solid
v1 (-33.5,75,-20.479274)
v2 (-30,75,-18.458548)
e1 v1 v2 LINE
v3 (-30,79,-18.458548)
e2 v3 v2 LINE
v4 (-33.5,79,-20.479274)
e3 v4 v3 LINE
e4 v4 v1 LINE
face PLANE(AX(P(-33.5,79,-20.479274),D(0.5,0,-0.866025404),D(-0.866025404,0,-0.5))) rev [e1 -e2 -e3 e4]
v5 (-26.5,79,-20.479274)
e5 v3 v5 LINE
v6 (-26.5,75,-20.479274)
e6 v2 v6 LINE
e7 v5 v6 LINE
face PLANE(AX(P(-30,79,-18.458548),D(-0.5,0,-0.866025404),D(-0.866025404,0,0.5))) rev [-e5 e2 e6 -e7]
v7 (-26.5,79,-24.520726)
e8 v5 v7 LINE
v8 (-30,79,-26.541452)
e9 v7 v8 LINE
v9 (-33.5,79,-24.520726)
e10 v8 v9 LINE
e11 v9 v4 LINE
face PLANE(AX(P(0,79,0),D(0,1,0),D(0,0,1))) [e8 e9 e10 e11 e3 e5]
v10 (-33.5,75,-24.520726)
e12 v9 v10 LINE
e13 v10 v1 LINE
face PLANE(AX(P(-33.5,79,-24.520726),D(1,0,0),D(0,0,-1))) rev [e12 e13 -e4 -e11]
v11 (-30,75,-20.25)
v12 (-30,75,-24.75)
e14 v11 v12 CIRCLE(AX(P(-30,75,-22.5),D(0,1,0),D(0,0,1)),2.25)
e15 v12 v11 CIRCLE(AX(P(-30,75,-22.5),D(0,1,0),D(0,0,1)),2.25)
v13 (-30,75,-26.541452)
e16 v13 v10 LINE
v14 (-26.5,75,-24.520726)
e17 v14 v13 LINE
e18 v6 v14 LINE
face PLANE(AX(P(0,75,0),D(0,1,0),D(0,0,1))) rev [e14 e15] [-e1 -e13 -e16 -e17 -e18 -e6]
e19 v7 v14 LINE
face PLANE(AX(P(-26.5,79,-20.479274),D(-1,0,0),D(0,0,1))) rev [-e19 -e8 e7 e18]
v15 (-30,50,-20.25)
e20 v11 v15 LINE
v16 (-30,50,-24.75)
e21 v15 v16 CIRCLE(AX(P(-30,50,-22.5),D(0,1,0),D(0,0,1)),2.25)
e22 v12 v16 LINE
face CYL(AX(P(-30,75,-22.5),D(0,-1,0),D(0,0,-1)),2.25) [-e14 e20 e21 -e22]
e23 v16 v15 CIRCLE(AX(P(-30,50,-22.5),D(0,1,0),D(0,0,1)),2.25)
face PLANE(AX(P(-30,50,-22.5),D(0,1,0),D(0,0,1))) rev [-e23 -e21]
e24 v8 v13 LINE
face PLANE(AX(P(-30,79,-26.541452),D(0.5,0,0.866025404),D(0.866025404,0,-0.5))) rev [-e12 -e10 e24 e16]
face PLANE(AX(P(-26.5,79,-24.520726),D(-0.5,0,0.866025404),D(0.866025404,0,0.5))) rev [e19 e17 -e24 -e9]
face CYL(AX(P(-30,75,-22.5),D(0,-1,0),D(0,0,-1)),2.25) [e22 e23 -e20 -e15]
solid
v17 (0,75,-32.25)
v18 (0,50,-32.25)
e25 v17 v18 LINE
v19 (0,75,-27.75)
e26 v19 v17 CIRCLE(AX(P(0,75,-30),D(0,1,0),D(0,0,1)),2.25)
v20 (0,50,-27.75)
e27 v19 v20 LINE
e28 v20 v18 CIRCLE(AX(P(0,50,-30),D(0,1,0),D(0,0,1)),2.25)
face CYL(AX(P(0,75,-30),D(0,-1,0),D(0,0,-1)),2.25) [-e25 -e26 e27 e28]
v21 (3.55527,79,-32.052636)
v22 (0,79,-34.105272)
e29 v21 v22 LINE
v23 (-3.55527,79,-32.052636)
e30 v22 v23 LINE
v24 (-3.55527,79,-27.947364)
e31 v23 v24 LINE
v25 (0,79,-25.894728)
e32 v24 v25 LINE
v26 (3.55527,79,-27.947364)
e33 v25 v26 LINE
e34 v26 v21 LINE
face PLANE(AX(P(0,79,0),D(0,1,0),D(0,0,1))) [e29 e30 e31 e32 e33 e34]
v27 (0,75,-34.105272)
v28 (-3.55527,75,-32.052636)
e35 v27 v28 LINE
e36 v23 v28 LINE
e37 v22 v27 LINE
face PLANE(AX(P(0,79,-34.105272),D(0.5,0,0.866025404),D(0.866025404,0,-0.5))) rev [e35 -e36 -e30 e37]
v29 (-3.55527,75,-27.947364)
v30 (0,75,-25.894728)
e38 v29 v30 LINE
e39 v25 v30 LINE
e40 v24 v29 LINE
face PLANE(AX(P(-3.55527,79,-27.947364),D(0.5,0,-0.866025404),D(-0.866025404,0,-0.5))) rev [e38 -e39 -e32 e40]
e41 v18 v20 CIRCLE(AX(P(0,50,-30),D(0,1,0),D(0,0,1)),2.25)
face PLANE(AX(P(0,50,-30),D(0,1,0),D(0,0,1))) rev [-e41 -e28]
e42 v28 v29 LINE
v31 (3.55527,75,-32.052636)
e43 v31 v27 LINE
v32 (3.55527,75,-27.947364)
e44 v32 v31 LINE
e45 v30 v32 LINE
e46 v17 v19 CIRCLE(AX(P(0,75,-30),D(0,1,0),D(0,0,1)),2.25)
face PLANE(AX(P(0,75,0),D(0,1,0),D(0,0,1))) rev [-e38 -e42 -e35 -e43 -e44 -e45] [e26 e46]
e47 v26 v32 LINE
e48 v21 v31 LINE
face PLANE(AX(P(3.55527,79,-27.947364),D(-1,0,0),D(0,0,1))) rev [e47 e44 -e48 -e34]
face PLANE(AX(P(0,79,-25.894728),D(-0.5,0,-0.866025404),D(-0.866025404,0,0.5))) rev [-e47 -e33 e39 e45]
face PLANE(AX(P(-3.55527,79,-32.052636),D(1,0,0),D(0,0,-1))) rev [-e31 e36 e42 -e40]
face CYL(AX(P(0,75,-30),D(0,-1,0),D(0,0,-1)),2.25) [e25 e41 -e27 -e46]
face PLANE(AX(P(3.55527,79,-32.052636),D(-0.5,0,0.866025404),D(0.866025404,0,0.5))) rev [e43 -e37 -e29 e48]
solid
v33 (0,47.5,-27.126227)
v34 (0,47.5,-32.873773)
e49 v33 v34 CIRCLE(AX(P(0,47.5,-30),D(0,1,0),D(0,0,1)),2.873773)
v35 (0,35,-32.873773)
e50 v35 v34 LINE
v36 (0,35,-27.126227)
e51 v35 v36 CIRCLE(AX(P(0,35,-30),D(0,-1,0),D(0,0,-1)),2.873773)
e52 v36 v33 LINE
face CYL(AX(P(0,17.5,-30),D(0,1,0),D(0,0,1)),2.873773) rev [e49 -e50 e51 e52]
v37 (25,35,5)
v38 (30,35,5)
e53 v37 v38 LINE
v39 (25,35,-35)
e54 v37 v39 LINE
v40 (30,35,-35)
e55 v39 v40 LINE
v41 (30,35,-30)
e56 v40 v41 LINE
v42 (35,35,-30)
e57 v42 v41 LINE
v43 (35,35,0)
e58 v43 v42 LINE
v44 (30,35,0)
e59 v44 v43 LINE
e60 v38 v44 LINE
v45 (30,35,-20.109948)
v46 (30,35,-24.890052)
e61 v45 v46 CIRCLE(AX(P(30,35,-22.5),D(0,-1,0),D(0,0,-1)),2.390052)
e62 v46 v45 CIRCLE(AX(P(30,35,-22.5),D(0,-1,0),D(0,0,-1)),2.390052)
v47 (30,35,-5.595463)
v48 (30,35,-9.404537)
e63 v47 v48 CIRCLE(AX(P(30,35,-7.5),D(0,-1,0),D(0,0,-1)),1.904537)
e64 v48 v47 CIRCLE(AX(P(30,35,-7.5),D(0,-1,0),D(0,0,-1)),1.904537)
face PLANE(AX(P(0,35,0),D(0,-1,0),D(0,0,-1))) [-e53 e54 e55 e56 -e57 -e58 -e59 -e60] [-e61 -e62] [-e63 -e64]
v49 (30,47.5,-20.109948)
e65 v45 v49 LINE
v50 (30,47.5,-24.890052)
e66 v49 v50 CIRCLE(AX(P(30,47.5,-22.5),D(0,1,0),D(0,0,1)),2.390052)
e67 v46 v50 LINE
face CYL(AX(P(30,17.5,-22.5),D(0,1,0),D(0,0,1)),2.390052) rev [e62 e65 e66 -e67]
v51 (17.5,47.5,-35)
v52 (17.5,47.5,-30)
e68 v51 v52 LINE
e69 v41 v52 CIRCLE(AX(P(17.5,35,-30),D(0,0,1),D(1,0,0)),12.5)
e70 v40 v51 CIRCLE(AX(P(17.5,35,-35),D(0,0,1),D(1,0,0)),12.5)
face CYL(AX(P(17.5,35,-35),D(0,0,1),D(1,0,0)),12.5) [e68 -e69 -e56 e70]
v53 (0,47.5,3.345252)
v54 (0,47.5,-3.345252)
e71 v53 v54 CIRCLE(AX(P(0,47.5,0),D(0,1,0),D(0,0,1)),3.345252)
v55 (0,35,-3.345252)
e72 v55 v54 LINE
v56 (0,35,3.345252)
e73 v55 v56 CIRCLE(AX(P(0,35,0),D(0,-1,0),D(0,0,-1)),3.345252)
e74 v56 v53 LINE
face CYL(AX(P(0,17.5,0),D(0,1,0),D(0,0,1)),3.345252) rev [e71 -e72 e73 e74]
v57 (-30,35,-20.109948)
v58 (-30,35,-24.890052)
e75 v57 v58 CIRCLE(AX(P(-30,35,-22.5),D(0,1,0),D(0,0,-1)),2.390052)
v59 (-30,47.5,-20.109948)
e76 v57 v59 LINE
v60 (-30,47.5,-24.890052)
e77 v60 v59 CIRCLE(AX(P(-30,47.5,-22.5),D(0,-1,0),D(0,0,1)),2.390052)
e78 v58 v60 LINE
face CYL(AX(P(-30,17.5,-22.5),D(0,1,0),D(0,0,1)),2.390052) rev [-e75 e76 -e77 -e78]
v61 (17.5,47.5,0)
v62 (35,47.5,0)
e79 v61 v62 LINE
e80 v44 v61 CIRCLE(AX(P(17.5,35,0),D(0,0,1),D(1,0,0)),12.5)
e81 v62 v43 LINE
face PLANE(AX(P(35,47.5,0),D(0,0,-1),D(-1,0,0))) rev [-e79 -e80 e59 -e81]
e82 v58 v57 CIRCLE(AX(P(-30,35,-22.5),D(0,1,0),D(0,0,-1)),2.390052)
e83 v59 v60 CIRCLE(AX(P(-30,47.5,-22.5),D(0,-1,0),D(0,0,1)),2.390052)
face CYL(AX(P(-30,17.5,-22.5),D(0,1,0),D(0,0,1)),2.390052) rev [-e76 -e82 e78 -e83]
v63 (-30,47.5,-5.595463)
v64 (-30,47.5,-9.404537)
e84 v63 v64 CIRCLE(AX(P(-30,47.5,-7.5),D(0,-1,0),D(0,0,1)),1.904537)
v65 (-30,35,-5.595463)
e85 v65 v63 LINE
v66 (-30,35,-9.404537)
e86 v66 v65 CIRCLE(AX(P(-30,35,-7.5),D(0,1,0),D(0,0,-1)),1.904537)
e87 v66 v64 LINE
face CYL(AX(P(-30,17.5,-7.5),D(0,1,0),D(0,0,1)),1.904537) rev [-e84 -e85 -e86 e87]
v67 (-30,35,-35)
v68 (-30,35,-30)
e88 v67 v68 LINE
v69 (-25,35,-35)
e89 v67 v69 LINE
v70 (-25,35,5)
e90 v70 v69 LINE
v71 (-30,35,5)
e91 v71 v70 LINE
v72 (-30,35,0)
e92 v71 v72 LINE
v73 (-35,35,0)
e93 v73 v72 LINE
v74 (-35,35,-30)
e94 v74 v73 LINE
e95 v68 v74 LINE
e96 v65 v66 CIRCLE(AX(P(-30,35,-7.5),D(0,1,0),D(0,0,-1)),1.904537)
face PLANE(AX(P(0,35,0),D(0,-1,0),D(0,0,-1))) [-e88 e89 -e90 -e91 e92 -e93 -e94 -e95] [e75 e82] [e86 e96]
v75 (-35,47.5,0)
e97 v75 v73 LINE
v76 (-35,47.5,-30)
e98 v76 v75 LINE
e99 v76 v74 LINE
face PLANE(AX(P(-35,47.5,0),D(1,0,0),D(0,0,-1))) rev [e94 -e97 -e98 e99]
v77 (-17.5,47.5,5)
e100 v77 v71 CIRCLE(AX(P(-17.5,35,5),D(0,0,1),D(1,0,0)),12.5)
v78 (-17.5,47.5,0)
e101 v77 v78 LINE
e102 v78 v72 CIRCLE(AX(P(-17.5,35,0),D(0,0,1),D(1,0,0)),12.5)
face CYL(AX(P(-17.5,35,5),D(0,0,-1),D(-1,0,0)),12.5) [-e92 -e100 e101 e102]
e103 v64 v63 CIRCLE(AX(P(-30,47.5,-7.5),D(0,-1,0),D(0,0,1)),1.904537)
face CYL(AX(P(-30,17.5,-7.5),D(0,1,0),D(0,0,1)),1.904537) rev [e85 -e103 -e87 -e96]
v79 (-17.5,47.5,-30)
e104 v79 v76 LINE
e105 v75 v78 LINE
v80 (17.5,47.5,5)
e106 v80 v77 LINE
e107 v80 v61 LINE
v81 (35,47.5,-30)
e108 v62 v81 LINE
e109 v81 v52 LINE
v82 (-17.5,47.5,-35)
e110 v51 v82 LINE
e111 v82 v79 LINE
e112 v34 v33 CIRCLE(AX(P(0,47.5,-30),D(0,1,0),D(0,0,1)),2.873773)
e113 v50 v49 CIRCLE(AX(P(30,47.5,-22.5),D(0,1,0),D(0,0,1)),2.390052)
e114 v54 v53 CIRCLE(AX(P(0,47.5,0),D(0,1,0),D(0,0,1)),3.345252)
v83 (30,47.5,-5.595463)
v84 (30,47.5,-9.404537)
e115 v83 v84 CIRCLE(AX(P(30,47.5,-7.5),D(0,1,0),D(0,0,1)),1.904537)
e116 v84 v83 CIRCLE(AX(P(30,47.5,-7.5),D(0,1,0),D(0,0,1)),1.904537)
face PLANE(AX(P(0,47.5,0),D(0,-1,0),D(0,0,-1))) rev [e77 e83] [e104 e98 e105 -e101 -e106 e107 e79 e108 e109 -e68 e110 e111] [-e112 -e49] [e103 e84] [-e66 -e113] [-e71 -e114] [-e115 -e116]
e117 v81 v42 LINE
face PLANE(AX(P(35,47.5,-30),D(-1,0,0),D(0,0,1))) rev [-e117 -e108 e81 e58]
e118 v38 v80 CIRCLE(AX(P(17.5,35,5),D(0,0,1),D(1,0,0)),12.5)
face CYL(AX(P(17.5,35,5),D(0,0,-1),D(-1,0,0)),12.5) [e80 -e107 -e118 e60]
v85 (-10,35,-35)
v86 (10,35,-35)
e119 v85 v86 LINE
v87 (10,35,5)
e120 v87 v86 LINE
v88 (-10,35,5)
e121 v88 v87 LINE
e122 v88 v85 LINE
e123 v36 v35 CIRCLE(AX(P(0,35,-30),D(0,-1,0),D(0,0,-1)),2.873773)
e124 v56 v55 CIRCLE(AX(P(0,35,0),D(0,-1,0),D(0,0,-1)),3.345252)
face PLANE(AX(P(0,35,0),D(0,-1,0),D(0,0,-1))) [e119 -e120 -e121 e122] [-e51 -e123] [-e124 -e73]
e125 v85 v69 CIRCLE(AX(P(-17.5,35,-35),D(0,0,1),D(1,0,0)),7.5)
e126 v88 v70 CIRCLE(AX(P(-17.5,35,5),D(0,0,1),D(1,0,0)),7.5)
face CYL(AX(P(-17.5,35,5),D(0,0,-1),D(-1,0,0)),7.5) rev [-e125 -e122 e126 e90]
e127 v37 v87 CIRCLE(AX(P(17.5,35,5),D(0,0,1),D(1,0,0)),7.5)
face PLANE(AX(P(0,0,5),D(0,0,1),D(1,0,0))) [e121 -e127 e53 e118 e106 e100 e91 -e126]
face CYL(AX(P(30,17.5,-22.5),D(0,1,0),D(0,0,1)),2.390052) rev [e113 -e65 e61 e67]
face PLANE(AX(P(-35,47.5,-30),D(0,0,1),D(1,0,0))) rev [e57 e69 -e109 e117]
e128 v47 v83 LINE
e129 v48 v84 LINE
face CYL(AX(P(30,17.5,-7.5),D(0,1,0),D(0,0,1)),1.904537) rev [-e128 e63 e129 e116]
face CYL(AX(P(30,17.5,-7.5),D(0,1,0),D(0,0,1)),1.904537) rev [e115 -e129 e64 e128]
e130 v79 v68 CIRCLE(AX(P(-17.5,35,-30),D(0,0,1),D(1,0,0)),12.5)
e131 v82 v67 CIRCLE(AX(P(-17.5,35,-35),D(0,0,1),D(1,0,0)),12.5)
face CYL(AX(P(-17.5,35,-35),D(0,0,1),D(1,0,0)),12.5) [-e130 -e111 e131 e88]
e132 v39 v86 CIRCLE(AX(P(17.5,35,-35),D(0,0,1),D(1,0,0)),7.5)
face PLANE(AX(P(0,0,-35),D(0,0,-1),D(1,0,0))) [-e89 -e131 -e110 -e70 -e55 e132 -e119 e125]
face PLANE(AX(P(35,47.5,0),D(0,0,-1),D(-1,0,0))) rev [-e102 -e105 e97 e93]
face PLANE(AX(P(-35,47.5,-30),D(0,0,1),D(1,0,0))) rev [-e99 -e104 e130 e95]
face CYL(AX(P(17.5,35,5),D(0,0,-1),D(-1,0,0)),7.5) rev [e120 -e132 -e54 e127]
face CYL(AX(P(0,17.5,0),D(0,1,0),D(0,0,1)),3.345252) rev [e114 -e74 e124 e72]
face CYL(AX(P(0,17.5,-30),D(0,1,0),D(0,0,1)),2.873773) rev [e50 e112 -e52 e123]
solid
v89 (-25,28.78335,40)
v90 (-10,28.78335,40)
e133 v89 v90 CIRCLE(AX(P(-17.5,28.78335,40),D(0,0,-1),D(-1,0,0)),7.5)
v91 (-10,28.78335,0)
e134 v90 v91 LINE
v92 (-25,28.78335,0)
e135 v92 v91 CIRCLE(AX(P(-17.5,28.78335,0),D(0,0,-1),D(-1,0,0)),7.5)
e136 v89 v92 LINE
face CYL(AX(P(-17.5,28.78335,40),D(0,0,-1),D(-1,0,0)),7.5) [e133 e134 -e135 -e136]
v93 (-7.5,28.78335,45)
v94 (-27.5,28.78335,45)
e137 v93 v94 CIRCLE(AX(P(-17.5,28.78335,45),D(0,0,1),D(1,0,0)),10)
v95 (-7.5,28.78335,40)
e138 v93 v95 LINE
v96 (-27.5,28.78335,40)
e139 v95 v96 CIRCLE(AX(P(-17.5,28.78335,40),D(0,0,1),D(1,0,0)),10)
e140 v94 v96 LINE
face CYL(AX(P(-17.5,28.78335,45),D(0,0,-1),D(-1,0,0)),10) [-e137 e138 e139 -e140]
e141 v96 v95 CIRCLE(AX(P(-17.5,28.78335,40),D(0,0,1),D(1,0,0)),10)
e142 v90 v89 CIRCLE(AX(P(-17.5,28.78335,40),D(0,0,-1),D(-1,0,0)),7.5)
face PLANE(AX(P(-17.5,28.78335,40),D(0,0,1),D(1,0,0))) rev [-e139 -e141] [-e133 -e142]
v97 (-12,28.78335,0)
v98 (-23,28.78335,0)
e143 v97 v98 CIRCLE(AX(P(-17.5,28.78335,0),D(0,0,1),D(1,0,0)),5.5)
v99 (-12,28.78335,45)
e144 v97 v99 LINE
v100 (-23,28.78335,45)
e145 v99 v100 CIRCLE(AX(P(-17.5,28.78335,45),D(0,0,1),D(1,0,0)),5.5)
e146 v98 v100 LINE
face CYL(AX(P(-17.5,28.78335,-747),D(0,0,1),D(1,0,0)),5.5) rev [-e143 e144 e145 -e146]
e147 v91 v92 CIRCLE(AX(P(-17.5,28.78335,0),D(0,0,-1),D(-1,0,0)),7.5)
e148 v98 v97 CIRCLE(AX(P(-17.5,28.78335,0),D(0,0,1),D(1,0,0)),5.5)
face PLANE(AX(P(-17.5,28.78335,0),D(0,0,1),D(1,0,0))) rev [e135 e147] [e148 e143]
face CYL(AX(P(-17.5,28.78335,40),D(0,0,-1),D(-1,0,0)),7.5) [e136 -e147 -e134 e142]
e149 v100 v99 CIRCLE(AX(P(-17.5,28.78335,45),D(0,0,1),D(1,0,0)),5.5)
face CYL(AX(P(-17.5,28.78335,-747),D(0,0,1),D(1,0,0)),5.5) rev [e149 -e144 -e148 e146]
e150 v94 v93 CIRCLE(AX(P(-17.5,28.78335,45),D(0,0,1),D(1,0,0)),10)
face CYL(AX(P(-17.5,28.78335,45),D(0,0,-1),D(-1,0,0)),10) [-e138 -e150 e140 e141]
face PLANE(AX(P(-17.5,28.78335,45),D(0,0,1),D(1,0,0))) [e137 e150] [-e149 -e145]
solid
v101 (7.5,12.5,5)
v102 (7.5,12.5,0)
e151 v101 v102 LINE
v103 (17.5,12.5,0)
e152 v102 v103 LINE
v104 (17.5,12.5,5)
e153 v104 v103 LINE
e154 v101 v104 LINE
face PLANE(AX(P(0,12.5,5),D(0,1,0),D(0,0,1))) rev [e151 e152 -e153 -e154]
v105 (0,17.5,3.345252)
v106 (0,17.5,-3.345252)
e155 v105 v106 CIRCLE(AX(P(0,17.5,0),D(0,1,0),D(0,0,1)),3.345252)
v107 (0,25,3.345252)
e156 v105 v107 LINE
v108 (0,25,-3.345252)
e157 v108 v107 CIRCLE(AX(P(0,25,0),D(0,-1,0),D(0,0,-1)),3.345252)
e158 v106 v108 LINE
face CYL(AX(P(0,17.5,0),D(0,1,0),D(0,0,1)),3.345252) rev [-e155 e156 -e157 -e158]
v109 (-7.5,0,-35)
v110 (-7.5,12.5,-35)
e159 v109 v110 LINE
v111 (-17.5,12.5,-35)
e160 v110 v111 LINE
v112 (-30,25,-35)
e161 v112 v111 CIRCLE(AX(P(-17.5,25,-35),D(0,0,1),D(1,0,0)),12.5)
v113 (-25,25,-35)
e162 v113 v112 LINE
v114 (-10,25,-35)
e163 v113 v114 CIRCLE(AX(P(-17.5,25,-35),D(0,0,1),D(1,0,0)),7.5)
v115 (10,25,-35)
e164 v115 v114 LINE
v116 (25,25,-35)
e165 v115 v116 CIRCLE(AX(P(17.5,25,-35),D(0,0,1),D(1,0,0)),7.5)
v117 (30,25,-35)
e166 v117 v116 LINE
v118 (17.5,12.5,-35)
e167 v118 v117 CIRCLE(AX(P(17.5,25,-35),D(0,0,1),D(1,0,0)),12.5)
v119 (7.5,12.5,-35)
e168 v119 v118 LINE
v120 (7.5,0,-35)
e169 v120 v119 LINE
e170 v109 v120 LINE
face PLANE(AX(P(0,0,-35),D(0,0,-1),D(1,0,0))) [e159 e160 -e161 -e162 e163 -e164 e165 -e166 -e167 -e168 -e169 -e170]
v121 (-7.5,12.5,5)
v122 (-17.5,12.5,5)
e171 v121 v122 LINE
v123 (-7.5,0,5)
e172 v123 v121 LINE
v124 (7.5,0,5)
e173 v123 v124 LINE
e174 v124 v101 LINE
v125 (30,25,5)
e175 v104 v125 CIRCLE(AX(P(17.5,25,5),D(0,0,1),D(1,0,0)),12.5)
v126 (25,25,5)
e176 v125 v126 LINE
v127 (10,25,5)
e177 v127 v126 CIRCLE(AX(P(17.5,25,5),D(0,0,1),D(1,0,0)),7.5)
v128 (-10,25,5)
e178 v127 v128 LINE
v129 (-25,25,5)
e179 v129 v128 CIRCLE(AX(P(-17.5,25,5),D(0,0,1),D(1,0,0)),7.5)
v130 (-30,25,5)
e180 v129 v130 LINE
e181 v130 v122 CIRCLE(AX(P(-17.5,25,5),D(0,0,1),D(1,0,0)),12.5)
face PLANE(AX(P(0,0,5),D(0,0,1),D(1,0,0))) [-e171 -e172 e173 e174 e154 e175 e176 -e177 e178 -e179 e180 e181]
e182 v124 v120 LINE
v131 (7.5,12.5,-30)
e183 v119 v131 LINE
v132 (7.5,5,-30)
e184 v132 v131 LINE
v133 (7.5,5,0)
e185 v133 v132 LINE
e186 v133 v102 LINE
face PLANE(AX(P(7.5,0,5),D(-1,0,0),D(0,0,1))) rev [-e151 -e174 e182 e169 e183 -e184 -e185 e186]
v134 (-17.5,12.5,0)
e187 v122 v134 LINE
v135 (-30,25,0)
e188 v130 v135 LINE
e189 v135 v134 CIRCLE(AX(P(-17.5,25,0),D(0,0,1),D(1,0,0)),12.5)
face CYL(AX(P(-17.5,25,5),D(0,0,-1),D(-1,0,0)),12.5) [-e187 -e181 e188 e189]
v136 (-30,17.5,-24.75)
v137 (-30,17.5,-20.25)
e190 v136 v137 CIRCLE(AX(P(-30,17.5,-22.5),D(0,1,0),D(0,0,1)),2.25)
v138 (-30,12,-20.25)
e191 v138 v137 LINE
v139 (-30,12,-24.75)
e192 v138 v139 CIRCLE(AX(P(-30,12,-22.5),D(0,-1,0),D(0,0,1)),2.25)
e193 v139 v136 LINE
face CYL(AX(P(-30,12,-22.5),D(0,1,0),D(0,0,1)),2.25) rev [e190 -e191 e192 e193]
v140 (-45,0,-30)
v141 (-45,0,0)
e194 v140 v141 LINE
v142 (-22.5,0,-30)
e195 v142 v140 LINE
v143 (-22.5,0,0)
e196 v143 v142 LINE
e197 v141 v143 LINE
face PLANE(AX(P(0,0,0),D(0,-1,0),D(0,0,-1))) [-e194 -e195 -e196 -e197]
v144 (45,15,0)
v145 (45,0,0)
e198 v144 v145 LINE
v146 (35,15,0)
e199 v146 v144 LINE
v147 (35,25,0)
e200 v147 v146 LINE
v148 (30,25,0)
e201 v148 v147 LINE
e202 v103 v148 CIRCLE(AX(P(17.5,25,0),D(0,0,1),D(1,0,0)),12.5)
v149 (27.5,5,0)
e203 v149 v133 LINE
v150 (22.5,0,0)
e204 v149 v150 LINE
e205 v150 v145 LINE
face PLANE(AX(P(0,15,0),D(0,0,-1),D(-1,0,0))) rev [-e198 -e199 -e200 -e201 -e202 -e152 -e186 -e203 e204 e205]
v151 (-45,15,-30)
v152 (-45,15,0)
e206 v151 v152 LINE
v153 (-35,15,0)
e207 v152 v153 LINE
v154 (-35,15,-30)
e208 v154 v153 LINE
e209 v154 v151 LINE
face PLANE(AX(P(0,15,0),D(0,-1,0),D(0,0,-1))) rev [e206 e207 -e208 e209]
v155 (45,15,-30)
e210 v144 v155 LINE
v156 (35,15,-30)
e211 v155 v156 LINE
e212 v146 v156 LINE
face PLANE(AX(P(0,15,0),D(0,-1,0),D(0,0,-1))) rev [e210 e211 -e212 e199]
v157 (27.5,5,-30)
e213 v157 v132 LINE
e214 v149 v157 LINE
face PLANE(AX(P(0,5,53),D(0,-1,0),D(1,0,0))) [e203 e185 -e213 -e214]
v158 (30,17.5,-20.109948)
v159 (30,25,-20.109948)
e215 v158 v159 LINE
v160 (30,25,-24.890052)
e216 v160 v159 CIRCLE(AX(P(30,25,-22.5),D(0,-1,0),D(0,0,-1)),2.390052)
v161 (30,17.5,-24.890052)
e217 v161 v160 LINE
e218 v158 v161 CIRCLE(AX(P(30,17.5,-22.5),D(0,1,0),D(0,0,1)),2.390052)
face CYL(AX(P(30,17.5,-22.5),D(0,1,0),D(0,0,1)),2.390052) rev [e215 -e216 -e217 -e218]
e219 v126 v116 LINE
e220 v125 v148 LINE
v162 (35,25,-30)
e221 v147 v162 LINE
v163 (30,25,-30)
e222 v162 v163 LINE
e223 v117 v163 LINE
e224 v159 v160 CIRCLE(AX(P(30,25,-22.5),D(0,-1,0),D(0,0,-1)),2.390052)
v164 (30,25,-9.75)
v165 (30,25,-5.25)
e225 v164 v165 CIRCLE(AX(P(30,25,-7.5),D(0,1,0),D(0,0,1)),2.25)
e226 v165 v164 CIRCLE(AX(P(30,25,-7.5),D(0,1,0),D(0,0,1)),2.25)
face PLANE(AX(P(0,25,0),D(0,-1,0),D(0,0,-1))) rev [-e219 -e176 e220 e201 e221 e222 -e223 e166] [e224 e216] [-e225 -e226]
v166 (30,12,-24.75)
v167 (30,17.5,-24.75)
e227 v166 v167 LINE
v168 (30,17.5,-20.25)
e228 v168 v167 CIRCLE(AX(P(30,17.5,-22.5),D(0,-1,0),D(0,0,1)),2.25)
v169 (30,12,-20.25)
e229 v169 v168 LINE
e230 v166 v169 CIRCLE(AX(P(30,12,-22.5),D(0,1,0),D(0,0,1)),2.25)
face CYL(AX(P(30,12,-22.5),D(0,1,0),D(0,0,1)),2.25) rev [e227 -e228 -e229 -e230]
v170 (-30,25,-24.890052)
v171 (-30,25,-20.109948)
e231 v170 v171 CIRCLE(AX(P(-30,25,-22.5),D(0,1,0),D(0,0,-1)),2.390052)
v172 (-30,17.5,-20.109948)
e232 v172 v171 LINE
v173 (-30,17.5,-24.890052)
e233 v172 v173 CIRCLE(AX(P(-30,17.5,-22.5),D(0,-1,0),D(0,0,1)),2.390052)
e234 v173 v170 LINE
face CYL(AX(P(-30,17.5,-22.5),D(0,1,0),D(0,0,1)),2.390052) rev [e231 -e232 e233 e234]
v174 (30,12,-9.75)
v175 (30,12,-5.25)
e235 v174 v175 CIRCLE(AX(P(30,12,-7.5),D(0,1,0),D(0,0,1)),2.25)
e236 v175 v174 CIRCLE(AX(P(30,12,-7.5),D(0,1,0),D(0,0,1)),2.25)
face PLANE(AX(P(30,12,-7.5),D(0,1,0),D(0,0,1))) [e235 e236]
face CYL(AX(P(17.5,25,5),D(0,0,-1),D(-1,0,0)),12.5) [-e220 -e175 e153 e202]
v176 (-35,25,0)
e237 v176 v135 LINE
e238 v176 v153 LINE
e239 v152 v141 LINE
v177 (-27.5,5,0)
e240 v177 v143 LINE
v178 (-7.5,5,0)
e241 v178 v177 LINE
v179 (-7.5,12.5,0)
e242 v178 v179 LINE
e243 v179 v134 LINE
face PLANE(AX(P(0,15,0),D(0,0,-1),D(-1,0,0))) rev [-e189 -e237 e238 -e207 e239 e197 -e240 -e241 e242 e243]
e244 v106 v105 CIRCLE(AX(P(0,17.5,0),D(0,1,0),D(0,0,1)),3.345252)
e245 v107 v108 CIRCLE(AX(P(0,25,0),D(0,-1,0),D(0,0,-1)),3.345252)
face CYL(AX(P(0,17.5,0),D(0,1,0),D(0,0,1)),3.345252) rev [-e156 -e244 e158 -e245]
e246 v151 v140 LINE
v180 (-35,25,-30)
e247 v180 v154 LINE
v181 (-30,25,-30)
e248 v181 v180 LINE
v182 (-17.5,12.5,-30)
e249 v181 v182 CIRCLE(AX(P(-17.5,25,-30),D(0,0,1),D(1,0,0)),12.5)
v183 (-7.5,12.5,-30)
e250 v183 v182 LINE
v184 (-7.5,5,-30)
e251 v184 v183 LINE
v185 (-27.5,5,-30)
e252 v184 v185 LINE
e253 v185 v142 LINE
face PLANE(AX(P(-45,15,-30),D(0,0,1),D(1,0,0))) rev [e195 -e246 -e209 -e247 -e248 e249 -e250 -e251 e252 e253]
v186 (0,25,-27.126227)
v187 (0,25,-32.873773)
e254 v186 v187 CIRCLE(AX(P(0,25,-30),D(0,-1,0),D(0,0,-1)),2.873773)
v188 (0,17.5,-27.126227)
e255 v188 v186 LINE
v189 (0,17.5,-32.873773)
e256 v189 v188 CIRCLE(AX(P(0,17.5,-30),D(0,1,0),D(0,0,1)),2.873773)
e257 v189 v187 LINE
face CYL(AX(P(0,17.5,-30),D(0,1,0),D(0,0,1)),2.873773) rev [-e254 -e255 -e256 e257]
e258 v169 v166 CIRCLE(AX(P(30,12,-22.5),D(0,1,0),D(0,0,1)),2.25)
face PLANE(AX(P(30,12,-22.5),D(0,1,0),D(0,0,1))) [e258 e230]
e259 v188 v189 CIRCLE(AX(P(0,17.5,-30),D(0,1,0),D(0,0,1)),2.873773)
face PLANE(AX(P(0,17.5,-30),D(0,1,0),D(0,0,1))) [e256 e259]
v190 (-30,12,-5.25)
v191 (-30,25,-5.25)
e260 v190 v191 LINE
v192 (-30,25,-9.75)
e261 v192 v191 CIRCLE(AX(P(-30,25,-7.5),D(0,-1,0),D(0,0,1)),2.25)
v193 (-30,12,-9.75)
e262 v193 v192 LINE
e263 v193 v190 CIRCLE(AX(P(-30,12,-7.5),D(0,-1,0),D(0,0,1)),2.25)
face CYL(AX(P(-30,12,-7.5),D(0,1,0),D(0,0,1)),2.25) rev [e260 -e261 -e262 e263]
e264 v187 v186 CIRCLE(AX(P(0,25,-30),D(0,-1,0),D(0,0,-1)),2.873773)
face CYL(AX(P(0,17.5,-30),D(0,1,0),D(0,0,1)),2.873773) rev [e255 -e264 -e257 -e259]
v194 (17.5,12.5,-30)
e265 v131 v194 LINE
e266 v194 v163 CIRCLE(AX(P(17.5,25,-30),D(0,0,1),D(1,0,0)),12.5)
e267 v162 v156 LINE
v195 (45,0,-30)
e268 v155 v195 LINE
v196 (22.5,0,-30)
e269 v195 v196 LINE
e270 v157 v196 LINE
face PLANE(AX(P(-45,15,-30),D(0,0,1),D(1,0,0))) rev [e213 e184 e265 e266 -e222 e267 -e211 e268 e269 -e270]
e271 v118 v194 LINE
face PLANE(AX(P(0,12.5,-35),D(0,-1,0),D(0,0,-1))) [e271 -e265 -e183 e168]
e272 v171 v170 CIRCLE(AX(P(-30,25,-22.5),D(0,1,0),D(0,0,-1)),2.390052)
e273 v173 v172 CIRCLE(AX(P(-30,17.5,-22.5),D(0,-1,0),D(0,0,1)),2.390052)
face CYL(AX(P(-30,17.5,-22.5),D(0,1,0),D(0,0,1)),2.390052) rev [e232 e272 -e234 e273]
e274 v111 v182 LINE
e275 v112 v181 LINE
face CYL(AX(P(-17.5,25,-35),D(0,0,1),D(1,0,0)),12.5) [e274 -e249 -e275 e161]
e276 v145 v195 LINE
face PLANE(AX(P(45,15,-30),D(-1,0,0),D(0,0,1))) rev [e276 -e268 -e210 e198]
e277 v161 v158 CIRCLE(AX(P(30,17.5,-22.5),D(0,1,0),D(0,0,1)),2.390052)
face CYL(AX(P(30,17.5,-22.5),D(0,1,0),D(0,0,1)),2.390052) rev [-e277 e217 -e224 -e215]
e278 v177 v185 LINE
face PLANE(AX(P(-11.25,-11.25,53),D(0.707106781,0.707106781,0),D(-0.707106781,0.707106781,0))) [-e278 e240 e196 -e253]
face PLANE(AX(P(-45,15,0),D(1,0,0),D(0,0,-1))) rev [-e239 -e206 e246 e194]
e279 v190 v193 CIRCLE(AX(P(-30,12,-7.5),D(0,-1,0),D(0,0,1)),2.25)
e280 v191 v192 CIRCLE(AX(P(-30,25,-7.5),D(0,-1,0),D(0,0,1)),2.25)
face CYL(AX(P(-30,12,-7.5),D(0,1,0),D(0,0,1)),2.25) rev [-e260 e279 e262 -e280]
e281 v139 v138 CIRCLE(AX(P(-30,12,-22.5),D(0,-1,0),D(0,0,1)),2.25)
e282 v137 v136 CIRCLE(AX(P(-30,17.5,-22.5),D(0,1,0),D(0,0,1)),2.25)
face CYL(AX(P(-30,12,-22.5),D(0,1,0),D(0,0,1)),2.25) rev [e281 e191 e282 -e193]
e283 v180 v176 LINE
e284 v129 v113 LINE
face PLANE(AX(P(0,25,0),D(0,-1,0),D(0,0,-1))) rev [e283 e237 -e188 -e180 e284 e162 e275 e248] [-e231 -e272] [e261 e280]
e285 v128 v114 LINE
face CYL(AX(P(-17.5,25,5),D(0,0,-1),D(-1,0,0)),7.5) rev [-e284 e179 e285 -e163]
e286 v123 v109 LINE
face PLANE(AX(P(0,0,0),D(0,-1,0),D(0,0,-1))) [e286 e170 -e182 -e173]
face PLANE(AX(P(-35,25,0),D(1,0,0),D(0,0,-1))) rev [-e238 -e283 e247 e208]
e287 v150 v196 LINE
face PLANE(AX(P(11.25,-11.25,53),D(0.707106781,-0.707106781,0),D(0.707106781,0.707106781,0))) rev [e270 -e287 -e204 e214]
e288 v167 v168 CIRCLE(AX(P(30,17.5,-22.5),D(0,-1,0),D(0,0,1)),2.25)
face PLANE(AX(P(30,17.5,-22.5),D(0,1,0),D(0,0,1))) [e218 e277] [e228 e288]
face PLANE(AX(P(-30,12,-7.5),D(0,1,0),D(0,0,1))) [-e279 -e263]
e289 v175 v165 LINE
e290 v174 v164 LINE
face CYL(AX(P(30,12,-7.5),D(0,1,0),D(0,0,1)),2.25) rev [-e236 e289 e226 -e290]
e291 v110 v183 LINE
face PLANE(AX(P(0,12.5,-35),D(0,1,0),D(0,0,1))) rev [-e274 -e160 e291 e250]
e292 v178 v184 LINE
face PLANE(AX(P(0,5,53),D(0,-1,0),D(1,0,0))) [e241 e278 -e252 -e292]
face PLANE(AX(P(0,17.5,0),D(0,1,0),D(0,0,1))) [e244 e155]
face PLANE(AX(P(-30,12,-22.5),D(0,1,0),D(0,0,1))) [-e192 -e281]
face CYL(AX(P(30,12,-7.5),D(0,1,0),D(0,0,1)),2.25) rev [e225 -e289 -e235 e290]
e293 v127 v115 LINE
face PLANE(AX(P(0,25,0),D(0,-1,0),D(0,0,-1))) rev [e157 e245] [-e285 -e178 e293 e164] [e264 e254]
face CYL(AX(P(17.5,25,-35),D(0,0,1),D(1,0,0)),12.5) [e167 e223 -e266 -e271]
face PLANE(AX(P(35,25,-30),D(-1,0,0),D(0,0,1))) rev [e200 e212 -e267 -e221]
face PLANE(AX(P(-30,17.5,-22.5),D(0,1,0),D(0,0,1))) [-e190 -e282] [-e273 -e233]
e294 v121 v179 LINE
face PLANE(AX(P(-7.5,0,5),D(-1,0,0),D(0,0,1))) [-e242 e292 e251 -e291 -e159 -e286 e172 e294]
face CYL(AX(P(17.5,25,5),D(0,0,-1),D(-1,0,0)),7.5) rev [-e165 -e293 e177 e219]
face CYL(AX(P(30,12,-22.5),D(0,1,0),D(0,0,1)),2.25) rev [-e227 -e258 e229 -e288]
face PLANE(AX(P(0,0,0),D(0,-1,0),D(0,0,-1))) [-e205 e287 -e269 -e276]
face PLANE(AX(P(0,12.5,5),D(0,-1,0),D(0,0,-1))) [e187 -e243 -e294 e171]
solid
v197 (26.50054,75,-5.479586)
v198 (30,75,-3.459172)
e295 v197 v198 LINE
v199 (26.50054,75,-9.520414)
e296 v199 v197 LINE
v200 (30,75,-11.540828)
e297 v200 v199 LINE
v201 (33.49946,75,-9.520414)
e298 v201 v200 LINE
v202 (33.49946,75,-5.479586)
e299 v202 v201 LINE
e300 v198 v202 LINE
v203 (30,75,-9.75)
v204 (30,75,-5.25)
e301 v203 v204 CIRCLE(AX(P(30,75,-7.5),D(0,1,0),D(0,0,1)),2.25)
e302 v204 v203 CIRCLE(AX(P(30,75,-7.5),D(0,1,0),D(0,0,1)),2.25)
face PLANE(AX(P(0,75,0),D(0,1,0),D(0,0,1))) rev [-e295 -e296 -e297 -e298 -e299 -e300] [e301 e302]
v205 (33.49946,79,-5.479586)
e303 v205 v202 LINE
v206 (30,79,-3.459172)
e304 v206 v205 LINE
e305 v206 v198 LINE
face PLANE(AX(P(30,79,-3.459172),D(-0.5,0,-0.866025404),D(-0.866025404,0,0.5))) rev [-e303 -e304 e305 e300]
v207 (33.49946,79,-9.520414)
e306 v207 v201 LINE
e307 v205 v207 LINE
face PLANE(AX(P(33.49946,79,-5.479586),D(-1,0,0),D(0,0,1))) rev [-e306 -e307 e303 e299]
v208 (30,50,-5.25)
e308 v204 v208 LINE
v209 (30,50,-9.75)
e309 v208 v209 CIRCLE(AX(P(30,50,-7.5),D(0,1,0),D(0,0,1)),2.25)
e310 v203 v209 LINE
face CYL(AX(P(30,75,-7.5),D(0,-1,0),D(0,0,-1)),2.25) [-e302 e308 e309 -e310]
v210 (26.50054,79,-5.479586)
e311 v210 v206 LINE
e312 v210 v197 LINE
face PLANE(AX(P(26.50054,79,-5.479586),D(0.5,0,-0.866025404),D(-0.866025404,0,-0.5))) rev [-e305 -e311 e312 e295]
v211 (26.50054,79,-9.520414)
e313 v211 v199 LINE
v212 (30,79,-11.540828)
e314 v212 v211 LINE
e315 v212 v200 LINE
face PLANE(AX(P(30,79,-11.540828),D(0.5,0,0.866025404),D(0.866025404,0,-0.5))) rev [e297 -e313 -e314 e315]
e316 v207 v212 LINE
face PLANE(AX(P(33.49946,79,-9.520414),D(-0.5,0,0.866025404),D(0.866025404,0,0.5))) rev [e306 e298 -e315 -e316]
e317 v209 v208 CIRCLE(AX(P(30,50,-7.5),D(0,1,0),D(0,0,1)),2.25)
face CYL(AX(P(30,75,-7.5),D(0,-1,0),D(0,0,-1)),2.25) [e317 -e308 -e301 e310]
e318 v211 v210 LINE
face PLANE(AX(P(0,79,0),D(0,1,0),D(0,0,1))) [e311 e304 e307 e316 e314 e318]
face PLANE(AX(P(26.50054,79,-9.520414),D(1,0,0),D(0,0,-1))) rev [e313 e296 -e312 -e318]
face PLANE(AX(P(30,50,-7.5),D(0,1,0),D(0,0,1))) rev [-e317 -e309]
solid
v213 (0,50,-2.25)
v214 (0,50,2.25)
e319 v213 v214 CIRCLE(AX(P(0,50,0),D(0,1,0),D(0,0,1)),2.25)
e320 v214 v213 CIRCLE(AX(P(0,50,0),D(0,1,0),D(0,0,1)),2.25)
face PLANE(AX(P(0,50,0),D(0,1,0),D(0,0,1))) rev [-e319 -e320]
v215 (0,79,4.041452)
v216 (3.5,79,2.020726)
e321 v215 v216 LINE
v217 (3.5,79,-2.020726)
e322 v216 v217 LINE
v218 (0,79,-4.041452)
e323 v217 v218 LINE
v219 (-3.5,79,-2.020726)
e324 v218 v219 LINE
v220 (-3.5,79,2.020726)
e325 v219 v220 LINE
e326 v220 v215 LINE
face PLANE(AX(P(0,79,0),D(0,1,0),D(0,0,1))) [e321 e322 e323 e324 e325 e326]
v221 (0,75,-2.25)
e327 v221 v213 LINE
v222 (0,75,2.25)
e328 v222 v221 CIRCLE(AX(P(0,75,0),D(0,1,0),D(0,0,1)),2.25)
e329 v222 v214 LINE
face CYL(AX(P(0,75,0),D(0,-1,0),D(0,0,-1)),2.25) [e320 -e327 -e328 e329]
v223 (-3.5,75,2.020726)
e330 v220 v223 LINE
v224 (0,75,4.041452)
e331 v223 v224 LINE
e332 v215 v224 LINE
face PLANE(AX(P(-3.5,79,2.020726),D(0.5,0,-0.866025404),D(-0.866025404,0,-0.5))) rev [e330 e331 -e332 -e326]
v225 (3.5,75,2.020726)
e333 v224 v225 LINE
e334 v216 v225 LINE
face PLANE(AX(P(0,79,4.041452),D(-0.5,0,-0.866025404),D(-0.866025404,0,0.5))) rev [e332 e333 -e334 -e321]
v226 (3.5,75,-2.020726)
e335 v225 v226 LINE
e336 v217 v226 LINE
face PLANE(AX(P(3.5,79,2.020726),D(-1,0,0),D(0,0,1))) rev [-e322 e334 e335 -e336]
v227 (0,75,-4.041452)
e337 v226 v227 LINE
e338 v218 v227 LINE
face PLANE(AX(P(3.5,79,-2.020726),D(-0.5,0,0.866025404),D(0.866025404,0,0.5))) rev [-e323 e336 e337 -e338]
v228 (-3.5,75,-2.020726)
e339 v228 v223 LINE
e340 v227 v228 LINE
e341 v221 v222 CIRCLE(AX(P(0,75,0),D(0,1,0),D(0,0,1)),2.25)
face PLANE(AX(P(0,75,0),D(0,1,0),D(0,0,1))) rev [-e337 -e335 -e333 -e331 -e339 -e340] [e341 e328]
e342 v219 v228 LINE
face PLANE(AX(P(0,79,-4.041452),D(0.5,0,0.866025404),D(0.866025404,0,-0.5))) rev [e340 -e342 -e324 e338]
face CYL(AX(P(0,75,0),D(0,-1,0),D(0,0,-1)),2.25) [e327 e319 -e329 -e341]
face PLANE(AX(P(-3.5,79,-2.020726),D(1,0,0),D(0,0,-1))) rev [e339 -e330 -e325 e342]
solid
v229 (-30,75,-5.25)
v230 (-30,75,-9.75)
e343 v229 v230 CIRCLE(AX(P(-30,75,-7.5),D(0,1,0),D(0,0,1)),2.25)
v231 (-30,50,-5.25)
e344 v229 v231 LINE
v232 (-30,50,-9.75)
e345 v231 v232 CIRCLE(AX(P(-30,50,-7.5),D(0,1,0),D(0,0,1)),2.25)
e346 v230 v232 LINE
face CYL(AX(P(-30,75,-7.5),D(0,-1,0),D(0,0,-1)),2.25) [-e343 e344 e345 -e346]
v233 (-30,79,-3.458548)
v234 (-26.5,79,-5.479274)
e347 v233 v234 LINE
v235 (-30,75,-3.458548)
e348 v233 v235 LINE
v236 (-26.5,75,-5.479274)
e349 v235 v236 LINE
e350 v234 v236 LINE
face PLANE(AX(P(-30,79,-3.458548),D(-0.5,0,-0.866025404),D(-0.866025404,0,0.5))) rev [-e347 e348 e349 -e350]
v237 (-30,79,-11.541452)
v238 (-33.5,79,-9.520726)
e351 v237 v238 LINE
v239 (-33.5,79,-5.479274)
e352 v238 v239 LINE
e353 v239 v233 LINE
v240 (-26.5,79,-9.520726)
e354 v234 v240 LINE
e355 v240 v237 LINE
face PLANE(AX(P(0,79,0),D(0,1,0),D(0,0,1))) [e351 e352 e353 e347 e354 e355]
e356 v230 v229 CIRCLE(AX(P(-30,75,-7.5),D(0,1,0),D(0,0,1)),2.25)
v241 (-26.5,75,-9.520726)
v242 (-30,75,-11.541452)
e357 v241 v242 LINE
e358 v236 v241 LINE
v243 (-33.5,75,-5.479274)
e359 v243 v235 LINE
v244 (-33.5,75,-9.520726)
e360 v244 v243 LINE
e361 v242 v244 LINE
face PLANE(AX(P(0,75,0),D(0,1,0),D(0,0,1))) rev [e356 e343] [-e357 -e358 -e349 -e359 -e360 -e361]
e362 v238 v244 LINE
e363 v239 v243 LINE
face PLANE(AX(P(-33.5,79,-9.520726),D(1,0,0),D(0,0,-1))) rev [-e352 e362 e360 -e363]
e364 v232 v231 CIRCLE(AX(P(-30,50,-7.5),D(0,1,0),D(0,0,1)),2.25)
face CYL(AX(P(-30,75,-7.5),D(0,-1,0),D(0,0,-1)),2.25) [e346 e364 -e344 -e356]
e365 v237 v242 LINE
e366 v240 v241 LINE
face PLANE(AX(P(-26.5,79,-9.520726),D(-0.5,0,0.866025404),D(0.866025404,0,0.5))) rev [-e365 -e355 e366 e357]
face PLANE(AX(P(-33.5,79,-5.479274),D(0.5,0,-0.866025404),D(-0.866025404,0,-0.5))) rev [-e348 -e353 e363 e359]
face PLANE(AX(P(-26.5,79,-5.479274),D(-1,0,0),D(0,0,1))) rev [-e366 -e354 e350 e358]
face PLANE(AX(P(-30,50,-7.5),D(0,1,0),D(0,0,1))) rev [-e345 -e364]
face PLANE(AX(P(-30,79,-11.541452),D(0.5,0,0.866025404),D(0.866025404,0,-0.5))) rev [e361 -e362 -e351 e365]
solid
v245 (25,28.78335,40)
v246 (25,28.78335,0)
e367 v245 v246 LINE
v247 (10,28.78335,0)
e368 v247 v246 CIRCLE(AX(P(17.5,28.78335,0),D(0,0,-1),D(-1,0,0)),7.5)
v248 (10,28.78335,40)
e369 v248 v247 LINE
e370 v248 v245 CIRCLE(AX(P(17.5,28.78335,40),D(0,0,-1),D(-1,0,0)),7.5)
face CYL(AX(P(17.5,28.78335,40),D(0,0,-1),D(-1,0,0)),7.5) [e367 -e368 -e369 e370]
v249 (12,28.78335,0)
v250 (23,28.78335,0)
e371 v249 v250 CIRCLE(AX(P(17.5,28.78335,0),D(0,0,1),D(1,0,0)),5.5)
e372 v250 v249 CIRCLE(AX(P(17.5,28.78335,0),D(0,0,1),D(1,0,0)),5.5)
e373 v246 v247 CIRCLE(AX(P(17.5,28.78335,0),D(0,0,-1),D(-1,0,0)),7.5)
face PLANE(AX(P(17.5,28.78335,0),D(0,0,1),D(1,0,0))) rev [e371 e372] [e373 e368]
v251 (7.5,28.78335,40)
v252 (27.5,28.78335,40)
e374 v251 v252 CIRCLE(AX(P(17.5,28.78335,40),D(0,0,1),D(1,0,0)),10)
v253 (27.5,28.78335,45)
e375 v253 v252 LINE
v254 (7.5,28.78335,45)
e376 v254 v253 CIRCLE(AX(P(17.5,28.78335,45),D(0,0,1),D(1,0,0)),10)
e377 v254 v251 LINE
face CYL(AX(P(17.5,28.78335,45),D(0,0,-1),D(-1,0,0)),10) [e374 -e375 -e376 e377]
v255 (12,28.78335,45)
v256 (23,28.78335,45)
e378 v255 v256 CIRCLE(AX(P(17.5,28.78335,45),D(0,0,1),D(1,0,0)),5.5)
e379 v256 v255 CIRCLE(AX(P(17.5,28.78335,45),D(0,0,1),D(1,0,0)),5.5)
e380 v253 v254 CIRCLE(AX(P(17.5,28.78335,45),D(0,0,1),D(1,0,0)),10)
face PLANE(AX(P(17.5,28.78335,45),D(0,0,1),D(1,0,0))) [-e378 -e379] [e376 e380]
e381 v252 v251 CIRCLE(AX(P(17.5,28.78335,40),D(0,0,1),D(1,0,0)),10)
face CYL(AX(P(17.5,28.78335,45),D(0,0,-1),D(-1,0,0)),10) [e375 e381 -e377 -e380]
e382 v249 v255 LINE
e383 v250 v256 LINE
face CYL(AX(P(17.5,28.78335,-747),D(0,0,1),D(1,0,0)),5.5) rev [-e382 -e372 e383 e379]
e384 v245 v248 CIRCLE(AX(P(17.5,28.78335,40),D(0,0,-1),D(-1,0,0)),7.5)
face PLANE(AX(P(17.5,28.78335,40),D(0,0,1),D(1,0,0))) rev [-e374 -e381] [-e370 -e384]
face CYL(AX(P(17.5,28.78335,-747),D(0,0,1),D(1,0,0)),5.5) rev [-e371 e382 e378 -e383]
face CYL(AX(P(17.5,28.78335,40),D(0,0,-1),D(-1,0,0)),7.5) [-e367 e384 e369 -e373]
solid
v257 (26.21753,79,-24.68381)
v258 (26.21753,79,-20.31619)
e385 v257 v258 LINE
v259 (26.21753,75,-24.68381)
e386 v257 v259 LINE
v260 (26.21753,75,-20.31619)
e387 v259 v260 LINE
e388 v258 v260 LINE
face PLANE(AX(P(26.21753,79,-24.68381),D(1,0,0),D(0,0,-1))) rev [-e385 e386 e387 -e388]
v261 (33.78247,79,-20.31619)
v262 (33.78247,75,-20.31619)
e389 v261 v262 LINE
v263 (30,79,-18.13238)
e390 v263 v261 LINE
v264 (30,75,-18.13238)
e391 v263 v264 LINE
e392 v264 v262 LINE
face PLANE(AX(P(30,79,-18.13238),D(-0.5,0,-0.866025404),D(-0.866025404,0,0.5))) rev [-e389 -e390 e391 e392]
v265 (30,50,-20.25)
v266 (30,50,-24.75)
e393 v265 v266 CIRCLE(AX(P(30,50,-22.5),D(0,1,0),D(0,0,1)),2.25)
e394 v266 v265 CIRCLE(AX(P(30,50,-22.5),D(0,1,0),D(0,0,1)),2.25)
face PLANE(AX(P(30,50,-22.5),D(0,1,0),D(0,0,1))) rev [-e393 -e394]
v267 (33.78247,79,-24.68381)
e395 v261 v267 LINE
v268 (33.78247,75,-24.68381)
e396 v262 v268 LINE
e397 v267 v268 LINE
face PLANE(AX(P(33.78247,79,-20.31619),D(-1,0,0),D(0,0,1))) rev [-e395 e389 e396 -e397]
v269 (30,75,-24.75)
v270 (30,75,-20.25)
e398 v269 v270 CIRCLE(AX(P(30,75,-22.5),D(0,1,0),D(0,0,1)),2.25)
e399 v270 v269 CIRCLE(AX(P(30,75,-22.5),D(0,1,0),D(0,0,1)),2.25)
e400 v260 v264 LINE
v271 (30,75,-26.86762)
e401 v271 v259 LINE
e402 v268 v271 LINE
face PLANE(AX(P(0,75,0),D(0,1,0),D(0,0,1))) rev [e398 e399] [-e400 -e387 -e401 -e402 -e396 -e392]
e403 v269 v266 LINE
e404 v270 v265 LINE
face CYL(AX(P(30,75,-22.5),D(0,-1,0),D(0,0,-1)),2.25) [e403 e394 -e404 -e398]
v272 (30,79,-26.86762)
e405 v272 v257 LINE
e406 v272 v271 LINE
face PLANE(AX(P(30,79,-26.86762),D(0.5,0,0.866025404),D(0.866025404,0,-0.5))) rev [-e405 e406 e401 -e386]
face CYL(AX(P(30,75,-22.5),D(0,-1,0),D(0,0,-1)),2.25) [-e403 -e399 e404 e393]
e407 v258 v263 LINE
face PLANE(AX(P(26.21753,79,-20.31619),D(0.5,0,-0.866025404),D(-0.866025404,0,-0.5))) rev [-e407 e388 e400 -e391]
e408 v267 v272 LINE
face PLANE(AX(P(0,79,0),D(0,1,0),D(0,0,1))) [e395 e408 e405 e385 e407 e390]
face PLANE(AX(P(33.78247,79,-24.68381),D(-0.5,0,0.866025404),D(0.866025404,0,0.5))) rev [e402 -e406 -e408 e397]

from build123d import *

# Parameters (mm, degrees)
BASE_BLOCK_DEPTH                 = 15
BASE_PEDESTAL_SKETCH_W           = 70
BASE_PEDESTAL_SKETCH_H           = 30
BASE_PEDESTAL_35X35_DEPTH        = 10
LOWER_JAW_HALF_DEPTH             = 5
LOWER_START                      = -83
LOWER_JAW_BORE_SKETCH_R          = 7.5
LOWER_JAW_BORE_DEPTH             = 83
LOWER_JAW_MIRRORED_BORE_DEPTH    = 83
BOLT_HOLES_SKETCH_R              = 2.25
BOLT_HOLES_2X_4_5_DEPTH          = 13
UPPER_CLAMP_BLOCK_SKETCH_W       = 70
UPPER_CLAMP_BLOCK_SKETCH_H       = 30
UPPER_CLAMP_BLOCK_DEPTH          = 12.5
UPPER_JAW_HALF_DEPTH             = 5
UPPER_JAW_BORE_SKETCH_R          = 7.5
UPPER_JAW_BORE_DEPTH             = 67
UPPER_BLOCK_CLEARANCE_SKETCH_R   = 2.390051805
UPPER_BLOCK_CLEARANCE_SKETCH_R_2 = 1.904536549
UPPER_BLOCK_CLEARANCE_SKETCH_R_3 = 2.873773491
UPPER_BLOCK_CLEARANCE_SKETCH_R_4 = 3.345251954
UPPER_BLOCK_CLEARANCE_CUT_DEPTH  = 30
BOLT_SHANKS_SKETCH_R             = 2.25
BOLT_SHANKS_6X_DEPTH             = 25
BOLT_SHANKS_6X_2_DEPTH           = 25
BOLT_SHANKS_6X_3_DEPTH           = 25
BOLT_SHANKS_6X_4_DEPTH           = 25
BOLT_SHANKS_6X_5_DEPTH           = 25
BOLT_SHANKS_6X_6_DEPTH           = 25
BOLT_HEADS_6X_HEX_DEPTH          = 4
SLEEVES_SKETCH_R                 = 5.5
SLEEVES_2X_DEPTH                 = 40
SLEEVES_2X_2_DEPTH               = 40
SLEEVE_FLANGES_SKETCH_R          = 10
SLEEVE_FLANGES_2X_DEPTH          = 5
SLEEVE_EXTENSIONS_SKETCH_R       = 7.5
SLEEVE_EXTENSIONS_2X_DEPTH       = 40
SLEEVE_BORES_SKETCH_R            = 5.5
SLEEVE_BORES_2X_DEPTH            = 792


with BuildPart() as part:
    # Base Block Sketch → Base Block (new body)
    with BuildSketch(Plane(origin=(0, 0, 0), x_dir=(1, 0, 0), z_dir=(0, 1, 0))):
        Polygon((0, 0), (45, 0), (45, 30), (-45, 30), (-45, 0), align=None)
    extrude(amount=BASE_BLOCK_DEPTH)

    # Base Pedestal Sketch → Base Pedestal 35x35 (add)
    with BuildSketch(Plane(origin=(0, 15, 0), x_dir=(1, 0, 0), z_dir=(0, 1, 0))):
        with Locations((0, 15)):
            Rectangle(BASE_PEDESTAL_SKETCH_W, BASE_PEDESTAL_SKETCH_H)
    extrude(amount=BASE_PEDESTAL_35X35_DEPTH)

    # Lower Jaw Sketch → Lower Jaw Half (add)
    with BuildSketch(Plane.XY):
        with BuildLine():
            Line((-25, 25), (-30, 25))
            ThreePointArc((-30, 25), (-26.338834765, 16.161165235), (-17.5, 12.5))
            Line((-17.5, 12.5), (-7.5, 12.5))
            Line((-7.5, 12.5), (-7.5, 0))
            Line((-7.5, 0), (0, 0))
            Line((0, 0), (7.5, 0))
            Line((7.5, 0), (7.5, 12.5))
            Line((7.5, 12.5), (17.5, 12.5))
            ThreePointArc((17.5, 12.5), (26.338834765, 16.161165235), (30, 25))
            Line((30, 25), (25, 25))
            ThreePointArc((25, 25), (17.5, 17.5), (10, 25))
            Line((10, 25), (-10, 25))
            ThreePointArc((-10, 25), (-17.5, 17.5), (-25, 25))
        make_face()
    lower_jaw_half = extrude(amount=LOWER_JAW_HALF_DEPTH)

    # Lower Jaw Bore Sketch → Lower Jaw Bore (cut)
    with BuildSketch(Plane.XY.offset(5).offset(LOWER_START)):
        with Locations((-17.5, 25)):
            Circle(LOWER_JAW_BORE_SKETCH_R)
        with Locations((17.5, 25)):
            Circle(LOWER_JAW_BORE_SKETCH_R)
    extrude(amount=LOWER_JAW_BORE_DEPTH, mode=Mode.SUBTRACT)

    # Lower Jaw Mirror: Lower Jaw Half across plane
    add(lower_jaw_half.mirror(Plane.XY.offset(-15)))

    # Lower Jaw Mirrored Bore Sketch → Lower Jaw Mirrored Bore (cut)
    with BuildSketch(Plane(origin=(0, 0, -30), x_dir=(-1, 0, 0), z_dir=(0, 0, -1))):
        Polygon((-27.5, 5), (-22.5, 0), (-7.5, 0), (-7.5, 5), align=None)
        Polygon((7.5, 5), (7.5, 0), (22.5, 0), (27.5, 5), align=None)
    extrude(amount=-LOWER_JAW_MIRRORED_BORE_DEPTH, mode=Mode.SUBTRACT)

    # Bolt Holes Sketch → Bolt Holes 2xØ4.5 (cut)
    with BuildSketch(Plane(origin=(0, 25, 0), x_dir=(1, 0, 0), z_dir=(0, 1, 0))):
        with Locations(Location((30, 7.5, 0), (0, 0, 270))):
            Circle(BOLT_HOLES_SKETCH_R)
        with Locations(Location((30, 22.5, 0), (0, 0, 270))):
            Circle(BOLT_HOLES_SKETCH_R)
    bolt_holes_2x_4_5 = extrude(amount=-BOLT_HOLES_2X_4_5_DEPTH, mode=Mode.SUBTRACT)

    # Bolt Holes Mirror: Bolt Holes 2xØ4.5 across plane
    add(bolt_holes_2x_4_5.mirror(Plane(origin=(0, 0, 0), x_dir=(0, 0, 1), z_dir=(1, 0, 0))), mode=Mode.SUBTRACT)


with BuildPart() as body_2:
    # Upper Clamp Block Sketch → Upper Clamp Block (new body)
    with BuildSketch(Plane(origin=(0, 35, 0), x_dir=(1, 0, 0), z_dir=(0, 1, 0))):
        with Locations((0, 15)):
            Rectangle(UPPER_CLAMP_BLOCK_SKETCH_W, UPPER_CLAMP_BLOCK_SKETCH_H)
    extrude(amount=UPPER_CLAMP_BLOCK_DEPTH)

    # Upper Jaw Sketch → Upper Jaw Half (add)
    with BuildSketch(Plane.XY):
        with BuildLine():
            ThreePointArc((-17.5, 47.5), (-26.338834765, 43.838834765), (-30, 35))
            Line((-30, 35), (-25, 35))
            ThreePointArc((-25, 35), (-17.5, 42.5), (-10, 35))
            Line((-10, 35), (-5, 35))
            Line((-5, 35), (5, 35))
            Line((5, 35), (10, 35))
            ThreePointArc((10, 35), (17.5, 42.5), (25, 35))
            Line((25, 35), (30, 35))
            ThreePointArc((30, 35), (26.338834765, 43.838834765), (17.5, 47.5))
            Line((17.5, 47.5), (-17.5, 47.5))
        make_face()
    upper_jaw_half = extrude(amount=UPPER_JAW_HALF_DEPTH)

    # Upper Jaw Bore Sketch → Upper Jaw Bore (cut)
    with BuildSketch(Plane.XY.offset(5)):
        with Locations((-17.5, 35)):
            Circle(UPPER_JAW_BORE_SKETCH_R)
        with Locations((17.5, 35)):
            Circle(UPPER_JAW_BORE_SKETCH_R)
    extrude(amount=-UPPER_JAW_BORE_DEPTH, mode=Mode.SUBTRACT)

    # Upper Jaw Mirror: Upper Jaw Half across plane
    add(upper_jaw_half.mirror(Plane.XY.offset(-15)))


with BuildPart() as upper_block_clearance_cut_tool:
    # Upper Block Clearance Sketch → Upper Block Clearance Cut (new body)
    with BuildSketch(Plane(origin=(0, 47.5, 0), x_dir=(1, 0, 0), z_dir=(0, 1, 0))):
        with Locations(Location((30, 22.5, 0), (0, 0, 270))):
            Circle(UPPER_BLOCK_CLEARANCE_SKETCH_R)
        with Locations(Location((30, 7.5, 0), (0, 0, 270))):
            Circle(UPPER_BLOCK_CLEARANCE_SKETCH_R_2)
        with Locations(Location((0, 30, 0), (0, 0, 270))):
            Circle(UPPER_BLOCK_CLEARANCE_SKETCH_R_3)
        with Locations(Location((0, 0, 0), (0, 0, 270))):
            Circle(UPPER_BLOCK_CLEARANCE_SKETCH_R_4)
    upper_block_clearance_cut = extrude(amount=-UPPER_BLOCK_CLEARANCE_CUT_DEPTH)


with BuildPart() as part_1:
    add(part.part)

    # Upper Block Clearance Cut: cut by upper_block_clearance_cut_tool
    add(upper_block_clearance_cut_tool.part, mode=Mode.SUBTRACT)


with BuildPart() as body_2_1:
    add(body_2.part)

    # Upper Block Clearance Cut: cut by upper_block_clearance_cut_tool
    add(upper_block_clearance_cut_tool.part, mode=Mode.SUBTRACT)


with BuildPart() as clamp_body_mirror_tool:
    # Clamp Body Mirror: Upper Block Clearance Cut across plane
    add(upper_block_clearance_cut.mirror(Plane(origin=(0, 0, 0), x_dir=(0, 0, 1), z_dir=(1, 0, 0))))


with BuildPart() as part_2:
    add(part_1.part)

    # Clamp Body Mirror: cut by clamp_body_mirror_tool
    add(clamp_body_mirror_tool.part, mode=Mode.SUBTRACT)


with BuildPart() as body_2_2:
    add(body_2_1.part)

    # Clamp Body Mirror: cut by clamp_body_mirror_tool
    add(clamp_body_mirror_tool.part, mode=Mode.SUBTRACT)


with BuildPart() as body_3:
    # Bolt Shanks Sketch → Bolt Shanks 6x (new body)
    with BuildSketch(Plane(origin=(0, 50, 0), x_dir=(1, 0, 0), z_dir=(0, 1, 0))):
        with Locations(Location((0, 0, 0), (0, 0, 270))):
            Circle(BOLT_SHANKS_SKETCH_R)
    extrude(amount=BOLT_SHANKS_6X_DEPTH)



with BuildPart() as body_4:
    # Bolt Shanks Sketch → Bolt Shanks 6x 2 (new body)
    with BuildSketch(Plane(origin=(0, 50, 0), x_dir=(1, 0, 0), z_dir=(0, 1, 0))):
        with Locations(Location((30, 22.5, 0), (0, 0, 270))):
            Circle(BOLT_SHANKS_SKETCH_R)
    extrude(amount=BOLT_SHANKS_6X_2_DEPTH)


with BuildPart() as body_5:
    # Bolt Shanks Sketch → Bolt Shanks 6x 3 (new body)
    with BuildSketch(Plane(origin=(0, 50, 0), x_dir=(1, 0, 0), z_dir=(0, 1, 0))):
        with Locations(Location((30, 7.5, 0), (0, 0, 270))):
            Circle(BOLT_SHANKS_SKETCH_R)
    extrude(amount=BOLT_SHANKS_6X_3_DEPTH)


with BuildPart() as body_6:
    # Bolt Shanks Sketch → Bolt Shanks 6x 4 (new body)
    with BuildSketch(Plane(origin=(0, 50, 0), x_dir=(1, 0, 0), z_dir=(0, 1, 0))):
        with Locations(Location((0, 30, 0), (0, 0, 270))):
            Circle(BOLT_SHANKS_SKETCH_R)
    extrude(amount=BOLT_SHANKS_6X_4_DEPTH)


with BuildPart() as body_7:
    # Bolt Shanks Sketch → Bolt Shanks 6x 5 (new body)
    with BuildSketch(Plane(origin=(0, 50, 0), x_dir=(1, 0, 0), z_dir=(0, 1, 0))):
        with Locations(Location((-30, 7.5, 0), (0, 0, 270))):
            Circle(BOLT_SHANKS_SKETCH_R)
    extrude(amount=BOLT_SHANKS_6X_5_DEPTH)


with BuildPart() as body_8:
    # Bolt Shanks Sketch → Bolt Shanks 6x 6 (new body)
    with BuildSketch(Plane(origin=(0, 50, 0), x_dir=(1, 0, 0), z_dir=(0, 1, 0))):
        with Locations(Location((-30, 22.5, 0), (0, 0, 270))):
            Circle(BOLT_SHANKS_SKETCH_R)
    extrude(amount=BOLT_SHANKS_6X_6_DEPTH)


with BuildPart() as body_3_1:
    add(body_3.part)

    add(body_4.part)  # Bolt Heads 6x Hex merges body 4

    add(body_5.part)  # Bolt Heads 6x Hex merges body 5

    add(body_6.part)  # Bolt Heads 6x Hex merges body 6

    add(body_7.part)  # Bolt Heads 6x Hex merges body 7

    add(body_8.part)  # Bolt Heads 6x Hex merges body 8
    # Bolt Heads Sketch → Bolt Heads 6x Hex (add)
    with BuildSketch(Plane(origin=(0, 75, 0), x_dir=(1, 0, 0), z_dir=(0, 1, 0))):
        Polygon((0, 34.105271911), (-3.555269764, 32.052635955), (-3.555269764, 27.947364045), (0, 25.894728089), (3.555269764, 27.947364045), (3.555269764, 32.052635955), align=None)
        Polygon((0, 4.041451884), (-3.5, 2.020725942), (-3.5, -2.020725942), (0, -4.041451884), (3.5, -2.020725942), (3.5, 2.020725942), align=None)
        Polygon((30, 26.867620156), (26.217529991, 24.683810078), (26.217529991, 20.316189922), (30, 18.132379844), (33.782470009, 20.316189922), (33.782470009, 24.683810078), align=None)
        Polygon((30, 11.540828206), (26.500540122, 9.520414103), (26.500540122, 5.479585897), (30, 3.459171794), (33.499459878, 5.479585897), (33.499459878, 9.520414103), align=None)
        Polygon((-30, 26.541451884), (-33.5, 24.520725942), (-33.5, 20.479274058), (-30, 18.458548116), (-26.5, 20.479274058), (-26.5, 24.520725942), align=None)
        Polygon((-30, 11.541451884), (-33.5, 9.520725942), (-33.5, 5.479274058), (-30, 3.458548116), (-26.5, 5.479274058), (-26.5, 9.520725942), align=None)
    extrude(amount=BOLT_HEADS_6X_HEX_DEPTH)


with BuildPart() as body_4_2:
    # Sleeves Sketch → Sleeves 2x (new body)
    with BuildSketch(Plane.XY):
        with Locations((-17.5, 28.783350127)):
            Circle(SLEEVES_SKETCH_R)
    extrude(amount=SLEEVES_2X_DEPTH)



with BuildPart() as body_5_2:
    # Sleeves Sketch → Sleeves 2x 2 (new body)
    with BuildSketch(Plane.XY):
        with Locations((17.5, 28.783350127)):
            Circle(SLEEVES_SKETCH_R)
    extrude(amount=SLEEVES_2X_2_DEPTH)


with BuildPart() as body_4_2_1:
    add(body_4_2.part)

    add(body_5_2.part)  # Sleeve Flanges 2x merges body 5 2
    # Sleeve Flanges Sketch → Sleeve Flanges 2x (add)
    with BuildSketch(Plane.XY.offset(40)):
        with Locations((-17.5, 28.783350127)):
            Circle(SLEEVE_FLANGES_SKETCH_R)
        with Locations((17.5, 28.783350127)):
            Circle(SLEEVE_FLANGES_SKETCH_R)
    extrude(amount=SLEEVE_FLANGES_2X_DEPTH)

    # Sleeve Extensions Sketch → Sleeve Extensions 2x (add)
    with BuildSketch(Plane(origin=(0, 0, 0), x_dir=(-1, 0, 0), z_dir=(0, 0, -1))):
        with Locations((-17.5, 28.783350127)):
            Circle(SLEEVE_EXTENSIONS_SKETCH_R)
        with Locations((17.5, 28.783350127)):
            Circle(SLEEVE_EXTENSIONS_SKETCH_R)
    extrude(amount=-SLEEVE_EXTENSIONS_2X_DEPTH)

    # Sleeve Bores Sketch → Sleeve Bores 2x (cut)
    with BuildSketch(Plane.XY.offset(45)):
        with Locations((-17.5, 28.783350127)):
            Circle(SLEEVE_BORES_SKETCH_R)
        with Locations((17.5, 28.783350127)):
            Circle(SLEEVE_BORES_SKETCH_R)
    extrude(amount=-SLEEVE_BORES_2X_DEPTH, mode=Mode.SUBTRACT)


solid = Compound([part_2.part, body_2_2.part, body_3_1.part, body_4_2_1.part])
